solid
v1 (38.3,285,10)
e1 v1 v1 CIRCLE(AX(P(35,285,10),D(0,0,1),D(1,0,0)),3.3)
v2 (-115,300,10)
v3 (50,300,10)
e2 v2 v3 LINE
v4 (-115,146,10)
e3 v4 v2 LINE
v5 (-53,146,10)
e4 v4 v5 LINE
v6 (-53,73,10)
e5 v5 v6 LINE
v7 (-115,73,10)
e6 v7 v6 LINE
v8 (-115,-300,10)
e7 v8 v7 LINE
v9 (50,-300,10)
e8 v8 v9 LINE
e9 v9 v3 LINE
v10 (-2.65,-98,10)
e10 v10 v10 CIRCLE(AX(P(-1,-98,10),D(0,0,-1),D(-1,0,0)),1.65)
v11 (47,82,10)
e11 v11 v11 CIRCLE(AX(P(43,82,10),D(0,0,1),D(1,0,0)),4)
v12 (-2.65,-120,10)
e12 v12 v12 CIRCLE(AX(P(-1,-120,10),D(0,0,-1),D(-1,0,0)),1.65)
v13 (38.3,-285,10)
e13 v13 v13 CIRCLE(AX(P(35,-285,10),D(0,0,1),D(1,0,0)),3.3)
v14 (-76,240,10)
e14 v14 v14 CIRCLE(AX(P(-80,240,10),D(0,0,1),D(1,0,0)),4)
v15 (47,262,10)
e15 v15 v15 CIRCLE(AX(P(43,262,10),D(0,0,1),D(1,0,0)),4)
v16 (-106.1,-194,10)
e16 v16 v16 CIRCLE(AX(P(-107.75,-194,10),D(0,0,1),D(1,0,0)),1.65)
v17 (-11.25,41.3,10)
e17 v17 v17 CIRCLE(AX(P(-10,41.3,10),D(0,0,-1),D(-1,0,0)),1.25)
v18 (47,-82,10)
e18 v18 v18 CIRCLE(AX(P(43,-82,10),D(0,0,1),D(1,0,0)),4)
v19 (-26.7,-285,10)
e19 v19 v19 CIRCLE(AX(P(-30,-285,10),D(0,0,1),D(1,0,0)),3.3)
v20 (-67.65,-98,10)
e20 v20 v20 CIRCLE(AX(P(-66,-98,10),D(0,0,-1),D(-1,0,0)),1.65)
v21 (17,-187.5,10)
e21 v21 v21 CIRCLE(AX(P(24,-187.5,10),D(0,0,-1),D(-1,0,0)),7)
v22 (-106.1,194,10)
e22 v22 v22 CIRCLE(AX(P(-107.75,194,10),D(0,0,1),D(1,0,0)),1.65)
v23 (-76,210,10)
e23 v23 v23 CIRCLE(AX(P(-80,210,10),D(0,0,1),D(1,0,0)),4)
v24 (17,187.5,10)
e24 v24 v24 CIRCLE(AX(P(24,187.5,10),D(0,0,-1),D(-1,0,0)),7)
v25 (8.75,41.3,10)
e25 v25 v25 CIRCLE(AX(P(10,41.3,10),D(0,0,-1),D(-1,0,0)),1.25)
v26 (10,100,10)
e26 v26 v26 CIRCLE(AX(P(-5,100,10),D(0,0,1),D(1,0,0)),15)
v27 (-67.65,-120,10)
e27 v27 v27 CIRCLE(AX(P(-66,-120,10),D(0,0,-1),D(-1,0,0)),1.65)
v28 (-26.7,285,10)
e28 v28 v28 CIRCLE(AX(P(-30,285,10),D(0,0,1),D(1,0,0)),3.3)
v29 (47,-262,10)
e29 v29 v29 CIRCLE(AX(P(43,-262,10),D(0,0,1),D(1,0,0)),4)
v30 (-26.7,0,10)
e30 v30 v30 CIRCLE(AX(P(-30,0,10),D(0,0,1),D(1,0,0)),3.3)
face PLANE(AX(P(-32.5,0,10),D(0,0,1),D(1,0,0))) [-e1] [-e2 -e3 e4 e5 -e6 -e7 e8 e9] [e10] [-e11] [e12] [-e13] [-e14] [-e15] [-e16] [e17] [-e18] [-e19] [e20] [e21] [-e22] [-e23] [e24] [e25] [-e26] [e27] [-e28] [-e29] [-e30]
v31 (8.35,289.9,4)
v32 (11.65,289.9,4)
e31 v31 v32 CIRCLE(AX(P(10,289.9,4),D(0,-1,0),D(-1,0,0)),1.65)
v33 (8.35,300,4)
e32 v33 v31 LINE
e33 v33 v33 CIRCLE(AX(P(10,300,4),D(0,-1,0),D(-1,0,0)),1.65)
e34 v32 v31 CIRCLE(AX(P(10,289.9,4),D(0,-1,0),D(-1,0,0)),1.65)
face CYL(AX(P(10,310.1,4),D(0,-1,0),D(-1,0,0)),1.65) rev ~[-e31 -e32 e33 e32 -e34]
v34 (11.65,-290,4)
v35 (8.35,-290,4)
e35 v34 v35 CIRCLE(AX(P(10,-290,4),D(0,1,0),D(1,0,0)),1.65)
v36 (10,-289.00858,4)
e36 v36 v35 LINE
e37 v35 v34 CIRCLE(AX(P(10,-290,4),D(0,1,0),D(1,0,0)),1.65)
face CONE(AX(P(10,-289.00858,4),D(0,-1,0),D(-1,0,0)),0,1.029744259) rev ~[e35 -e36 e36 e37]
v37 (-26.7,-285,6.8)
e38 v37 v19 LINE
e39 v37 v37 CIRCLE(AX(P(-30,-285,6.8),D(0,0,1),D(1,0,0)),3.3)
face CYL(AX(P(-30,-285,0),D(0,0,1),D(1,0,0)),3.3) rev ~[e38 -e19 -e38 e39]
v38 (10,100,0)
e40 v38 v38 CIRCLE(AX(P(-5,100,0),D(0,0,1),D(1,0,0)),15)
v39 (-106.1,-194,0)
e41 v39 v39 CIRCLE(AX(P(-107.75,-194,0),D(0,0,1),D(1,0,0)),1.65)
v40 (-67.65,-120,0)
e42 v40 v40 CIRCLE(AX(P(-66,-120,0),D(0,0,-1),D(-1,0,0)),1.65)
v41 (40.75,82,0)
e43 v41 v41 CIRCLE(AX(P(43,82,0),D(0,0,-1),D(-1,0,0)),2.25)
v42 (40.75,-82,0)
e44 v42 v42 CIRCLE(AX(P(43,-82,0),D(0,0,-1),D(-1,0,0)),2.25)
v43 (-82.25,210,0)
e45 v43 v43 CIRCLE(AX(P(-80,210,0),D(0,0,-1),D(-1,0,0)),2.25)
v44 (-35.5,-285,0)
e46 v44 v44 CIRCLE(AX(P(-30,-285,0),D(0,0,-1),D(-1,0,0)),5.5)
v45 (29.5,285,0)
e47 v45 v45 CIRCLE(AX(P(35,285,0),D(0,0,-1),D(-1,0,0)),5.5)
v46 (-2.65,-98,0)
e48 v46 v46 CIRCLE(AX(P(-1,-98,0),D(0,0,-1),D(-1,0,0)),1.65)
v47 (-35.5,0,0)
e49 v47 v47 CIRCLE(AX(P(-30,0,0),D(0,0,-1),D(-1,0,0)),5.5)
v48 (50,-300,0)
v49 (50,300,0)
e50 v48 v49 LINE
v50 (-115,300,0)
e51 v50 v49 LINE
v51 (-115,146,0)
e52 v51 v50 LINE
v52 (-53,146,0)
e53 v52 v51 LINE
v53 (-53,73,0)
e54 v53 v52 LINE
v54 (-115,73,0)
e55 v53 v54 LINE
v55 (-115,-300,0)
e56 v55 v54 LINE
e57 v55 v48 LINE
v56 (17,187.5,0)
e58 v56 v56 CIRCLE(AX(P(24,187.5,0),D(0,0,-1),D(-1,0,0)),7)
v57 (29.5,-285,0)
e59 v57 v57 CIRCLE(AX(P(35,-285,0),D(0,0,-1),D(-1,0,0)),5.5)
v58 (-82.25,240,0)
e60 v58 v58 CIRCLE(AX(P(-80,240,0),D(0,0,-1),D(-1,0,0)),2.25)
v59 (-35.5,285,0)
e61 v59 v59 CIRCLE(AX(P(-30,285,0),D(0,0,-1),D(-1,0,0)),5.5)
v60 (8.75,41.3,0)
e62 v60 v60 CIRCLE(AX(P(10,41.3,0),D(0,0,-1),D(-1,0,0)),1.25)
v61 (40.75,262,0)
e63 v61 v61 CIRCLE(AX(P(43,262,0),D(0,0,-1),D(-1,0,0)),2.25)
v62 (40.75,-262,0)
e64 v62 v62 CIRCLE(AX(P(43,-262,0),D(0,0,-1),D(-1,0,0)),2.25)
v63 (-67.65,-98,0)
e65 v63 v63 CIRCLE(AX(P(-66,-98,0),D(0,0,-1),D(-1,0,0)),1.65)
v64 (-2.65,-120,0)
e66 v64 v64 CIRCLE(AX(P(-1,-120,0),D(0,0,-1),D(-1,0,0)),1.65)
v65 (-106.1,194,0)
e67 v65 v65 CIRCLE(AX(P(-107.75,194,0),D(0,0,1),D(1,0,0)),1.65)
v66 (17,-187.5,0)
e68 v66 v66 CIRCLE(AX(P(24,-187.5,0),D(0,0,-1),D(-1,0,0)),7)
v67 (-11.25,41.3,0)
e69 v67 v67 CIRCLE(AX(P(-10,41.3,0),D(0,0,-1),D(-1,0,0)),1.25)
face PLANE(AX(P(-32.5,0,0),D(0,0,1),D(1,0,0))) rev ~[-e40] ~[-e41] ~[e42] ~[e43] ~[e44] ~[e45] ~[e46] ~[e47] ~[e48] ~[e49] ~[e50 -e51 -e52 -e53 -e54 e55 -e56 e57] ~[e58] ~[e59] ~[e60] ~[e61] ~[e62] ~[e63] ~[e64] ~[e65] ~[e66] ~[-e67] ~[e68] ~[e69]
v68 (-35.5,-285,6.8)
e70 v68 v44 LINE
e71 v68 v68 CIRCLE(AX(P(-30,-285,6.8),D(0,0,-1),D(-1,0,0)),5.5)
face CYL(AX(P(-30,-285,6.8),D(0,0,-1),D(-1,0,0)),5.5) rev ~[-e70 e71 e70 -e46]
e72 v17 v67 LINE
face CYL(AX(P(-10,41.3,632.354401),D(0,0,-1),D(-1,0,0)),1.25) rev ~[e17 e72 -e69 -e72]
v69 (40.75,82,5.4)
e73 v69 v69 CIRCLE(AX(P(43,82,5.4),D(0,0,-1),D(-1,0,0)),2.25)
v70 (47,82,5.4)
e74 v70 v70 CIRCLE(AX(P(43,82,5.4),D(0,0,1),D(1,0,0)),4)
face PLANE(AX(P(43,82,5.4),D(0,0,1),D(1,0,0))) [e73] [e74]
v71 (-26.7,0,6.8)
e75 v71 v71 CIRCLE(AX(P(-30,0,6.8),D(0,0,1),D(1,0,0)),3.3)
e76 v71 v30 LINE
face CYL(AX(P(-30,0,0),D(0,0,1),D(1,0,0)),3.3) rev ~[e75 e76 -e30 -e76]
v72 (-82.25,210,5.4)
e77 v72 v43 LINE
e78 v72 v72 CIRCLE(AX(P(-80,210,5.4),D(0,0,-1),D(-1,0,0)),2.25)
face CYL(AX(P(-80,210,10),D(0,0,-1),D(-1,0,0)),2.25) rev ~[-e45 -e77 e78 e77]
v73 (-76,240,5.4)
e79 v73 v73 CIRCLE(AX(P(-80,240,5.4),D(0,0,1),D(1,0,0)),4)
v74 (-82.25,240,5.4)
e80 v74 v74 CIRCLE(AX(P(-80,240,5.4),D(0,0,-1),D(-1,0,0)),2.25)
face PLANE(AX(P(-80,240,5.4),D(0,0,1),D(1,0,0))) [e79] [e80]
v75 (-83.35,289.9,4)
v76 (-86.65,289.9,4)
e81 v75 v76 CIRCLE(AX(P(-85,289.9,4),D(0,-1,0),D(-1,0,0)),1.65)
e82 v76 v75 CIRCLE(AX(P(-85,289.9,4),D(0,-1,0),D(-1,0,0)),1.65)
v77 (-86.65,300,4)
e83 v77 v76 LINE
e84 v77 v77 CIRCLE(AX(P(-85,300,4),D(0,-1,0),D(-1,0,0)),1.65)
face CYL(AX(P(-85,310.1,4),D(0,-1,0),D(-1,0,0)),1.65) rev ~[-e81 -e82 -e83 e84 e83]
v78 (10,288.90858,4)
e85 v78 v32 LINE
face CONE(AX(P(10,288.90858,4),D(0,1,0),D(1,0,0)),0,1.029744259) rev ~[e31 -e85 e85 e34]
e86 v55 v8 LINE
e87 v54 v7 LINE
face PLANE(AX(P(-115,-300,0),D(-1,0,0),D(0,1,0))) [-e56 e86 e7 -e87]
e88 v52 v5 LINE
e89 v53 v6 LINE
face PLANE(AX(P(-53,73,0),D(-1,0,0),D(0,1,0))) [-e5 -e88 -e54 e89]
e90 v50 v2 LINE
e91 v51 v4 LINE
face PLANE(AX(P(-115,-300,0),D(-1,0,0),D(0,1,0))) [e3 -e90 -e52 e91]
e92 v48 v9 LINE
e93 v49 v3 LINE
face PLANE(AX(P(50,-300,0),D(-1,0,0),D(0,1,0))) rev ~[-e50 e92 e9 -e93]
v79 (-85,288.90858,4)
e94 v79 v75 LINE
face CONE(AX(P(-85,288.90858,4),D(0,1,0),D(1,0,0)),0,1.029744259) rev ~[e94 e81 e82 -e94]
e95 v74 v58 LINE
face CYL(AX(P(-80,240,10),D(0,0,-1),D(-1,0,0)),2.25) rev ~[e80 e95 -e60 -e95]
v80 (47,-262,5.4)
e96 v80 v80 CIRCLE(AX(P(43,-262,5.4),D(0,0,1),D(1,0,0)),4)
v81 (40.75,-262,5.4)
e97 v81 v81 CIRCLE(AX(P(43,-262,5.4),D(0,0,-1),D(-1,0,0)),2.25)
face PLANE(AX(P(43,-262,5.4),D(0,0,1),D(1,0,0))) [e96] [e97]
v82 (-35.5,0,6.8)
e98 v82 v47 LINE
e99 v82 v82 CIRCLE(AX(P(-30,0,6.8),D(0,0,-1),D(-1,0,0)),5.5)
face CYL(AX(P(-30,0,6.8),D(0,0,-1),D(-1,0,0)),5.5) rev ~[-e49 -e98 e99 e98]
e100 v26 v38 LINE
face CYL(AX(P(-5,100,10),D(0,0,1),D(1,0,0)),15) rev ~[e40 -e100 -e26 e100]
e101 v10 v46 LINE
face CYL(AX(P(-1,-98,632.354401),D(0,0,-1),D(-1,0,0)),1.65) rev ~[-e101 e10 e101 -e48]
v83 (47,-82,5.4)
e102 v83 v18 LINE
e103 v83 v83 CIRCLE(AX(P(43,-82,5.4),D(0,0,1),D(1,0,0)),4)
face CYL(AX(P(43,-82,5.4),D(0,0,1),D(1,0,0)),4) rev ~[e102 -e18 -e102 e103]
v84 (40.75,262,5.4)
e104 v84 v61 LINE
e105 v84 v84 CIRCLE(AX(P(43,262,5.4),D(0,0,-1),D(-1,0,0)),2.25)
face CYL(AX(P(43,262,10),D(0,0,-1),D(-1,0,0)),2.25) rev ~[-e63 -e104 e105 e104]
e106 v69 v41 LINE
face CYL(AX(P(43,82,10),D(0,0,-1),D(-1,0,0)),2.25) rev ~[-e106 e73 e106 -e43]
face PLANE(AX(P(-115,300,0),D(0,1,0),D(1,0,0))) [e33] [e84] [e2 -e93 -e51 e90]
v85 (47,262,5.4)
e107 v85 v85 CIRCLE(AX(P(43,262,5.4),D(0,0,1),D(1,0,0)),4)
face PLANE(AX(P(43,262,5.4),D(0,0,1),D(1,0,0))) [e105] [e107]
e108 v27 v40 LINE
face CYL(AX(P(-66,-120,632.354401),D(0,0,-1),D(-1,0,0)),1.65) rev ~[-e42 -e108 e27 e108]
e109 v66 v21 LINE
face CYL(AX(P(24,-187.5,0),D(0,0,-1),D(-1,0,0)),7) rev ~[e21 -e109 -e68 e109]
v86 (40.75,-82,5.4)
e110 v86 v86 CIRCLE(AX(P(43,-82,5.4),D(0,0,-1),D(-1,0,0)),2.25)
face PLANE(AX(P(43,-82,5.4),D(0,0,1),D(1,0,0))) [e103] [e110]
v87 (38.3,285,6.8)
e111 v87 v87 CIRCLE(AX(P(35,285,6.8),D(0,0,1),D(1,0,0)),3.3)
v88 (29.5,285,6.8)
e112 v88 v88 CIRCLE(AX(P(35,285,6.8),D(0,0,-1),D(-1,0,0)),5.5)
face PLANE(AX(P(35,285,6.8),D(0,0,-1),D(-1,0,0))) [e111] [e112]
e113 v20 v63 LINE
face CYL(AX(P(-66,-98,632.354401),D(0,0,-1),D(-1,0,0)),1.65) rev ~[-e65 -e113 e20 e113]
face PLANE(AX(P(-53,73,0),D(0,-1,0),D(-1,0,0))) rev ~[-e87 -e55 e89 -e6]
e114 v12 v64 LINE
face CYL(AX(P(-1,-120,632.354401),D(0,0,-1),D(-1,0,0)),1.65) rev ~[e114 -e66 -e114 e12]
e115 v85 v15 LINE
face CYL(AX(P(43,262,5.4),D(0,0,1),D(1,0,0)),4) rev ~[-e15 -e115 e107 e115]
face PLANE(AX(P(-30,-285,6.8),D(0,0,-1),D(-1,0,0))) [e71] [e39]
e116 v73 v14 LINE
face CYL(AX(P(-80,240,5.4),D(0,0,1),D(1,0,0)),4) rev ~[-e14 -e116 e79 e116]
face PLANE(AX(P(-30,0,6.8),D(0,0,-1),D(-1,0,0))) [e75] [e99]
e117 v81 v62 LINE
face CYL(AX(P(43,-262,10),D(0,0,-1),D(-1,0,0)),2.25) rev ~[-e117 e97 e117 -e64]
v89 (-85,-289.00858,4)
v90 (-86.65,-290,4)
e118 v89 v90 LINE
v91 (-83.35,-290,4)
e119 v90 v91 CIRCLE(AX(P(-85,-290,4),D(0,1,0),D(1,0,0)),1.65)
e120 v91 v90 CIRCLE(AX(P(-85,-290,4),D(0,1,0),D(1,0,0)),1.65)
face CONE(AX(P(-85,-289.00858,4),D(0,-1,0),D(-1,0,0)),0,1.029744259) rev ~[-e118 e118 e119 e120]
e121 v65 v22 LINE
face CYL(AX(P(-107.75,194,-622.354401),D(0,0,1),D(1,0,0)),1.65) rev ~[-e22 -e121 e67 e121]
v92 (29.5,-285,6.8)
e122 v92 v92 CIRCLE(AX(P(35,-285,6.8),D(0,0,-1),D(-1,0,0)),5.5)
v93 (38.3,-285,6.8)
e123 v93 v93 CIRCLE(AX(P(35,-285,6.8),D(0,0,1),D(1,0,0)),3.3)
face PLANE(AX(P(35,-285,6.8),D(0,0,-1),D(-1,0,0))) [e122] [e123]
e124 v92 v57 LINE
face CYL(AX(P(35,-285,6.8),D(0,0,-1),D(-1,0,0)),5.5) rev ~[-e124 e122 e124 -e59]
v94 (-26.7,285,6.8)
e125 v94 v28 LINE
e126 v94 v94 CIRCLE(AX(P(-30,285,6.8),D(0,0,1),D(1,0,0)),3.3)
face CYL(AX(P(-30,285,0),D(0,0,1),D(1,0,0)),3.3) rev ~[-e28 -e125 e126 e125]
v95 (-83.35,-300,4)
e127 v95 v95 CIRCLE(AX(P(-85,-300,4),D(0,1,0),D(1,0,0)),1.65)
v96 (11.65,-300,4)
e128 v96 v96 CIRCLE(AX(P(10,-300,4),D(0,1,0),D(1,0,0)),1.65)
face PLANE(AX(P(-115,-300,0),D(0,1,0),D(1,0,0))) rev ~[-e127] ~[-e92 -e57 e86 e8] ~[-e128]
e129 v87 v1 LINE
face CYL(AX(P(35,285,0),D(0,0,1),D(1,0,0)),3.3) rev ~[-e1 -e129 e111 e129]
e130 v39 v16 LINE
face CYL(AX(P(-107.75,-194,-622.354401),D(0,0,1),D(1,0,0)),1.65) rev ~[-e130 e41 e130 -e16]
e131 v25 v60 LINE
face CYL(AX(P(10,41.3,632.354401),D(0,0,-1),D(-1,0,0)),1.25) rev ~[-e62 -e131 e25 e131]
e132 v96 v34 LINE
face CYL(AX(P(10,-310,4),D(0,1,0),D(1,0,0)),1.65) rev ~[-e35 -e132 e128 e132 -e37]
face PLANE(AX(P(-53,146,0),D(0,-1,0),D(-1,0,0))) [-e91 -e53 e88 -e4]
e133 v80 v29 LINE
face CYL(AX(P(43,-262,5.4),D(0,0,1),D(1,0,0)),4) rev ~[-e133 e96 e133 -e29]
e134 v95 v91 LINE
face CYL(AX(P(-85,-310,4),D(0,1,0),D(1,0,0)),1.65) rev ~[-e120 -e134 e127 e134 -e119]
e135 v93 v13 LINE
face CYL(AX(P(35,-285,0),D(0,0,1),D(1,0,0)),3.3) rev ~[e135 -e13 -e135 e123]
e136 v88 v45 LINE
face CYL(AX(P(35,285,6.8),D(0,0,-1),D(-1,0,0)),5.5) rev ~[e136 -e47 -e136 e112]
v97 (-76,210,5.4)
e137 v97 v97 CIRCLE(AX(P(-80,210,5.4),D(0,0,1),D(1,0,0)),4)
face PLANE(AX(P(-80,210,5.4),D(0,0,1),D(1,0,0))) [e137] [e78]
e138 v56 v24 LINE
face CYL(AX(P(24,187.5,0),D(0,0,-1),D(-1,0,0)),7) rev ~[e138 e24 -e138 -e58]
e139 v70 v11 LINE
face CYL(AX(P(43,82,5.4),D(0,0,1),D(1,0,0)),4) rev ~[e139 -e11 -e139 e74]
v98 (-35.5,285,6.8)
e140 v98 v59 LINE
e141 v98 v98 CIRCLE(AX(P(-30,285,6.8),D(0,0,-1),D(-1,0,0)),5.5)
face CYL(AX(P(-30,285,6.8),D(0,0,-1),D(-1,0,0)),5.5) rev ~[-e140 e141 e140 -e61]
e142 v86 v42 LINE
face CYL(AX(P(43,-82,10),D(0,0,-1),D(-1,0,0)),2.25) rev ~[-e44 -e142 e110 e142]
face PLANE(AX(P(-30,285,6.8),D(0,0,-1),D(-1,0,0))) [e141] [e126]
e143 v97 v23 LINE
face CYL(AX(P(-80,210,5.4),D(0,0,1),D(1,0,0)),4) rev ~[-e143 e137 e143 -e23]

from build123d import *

# Parameters (mm, degrees)
SKETCH_1_W                  = 165
SKETCH_1_H                  = 600
EXTRUDE_1_DEPTH             = 10
SKETCH_5_R                  = 15
CUT_EXTRUDE_1_DEPTH         = 322.442063209
HOLE_WIZARD_M4_1_D          = 3.3
HOLE_WIZARD_M3_1_D          = 2.5
HOLE_WIZARD_M4_3_D          = 3.3
SKETCH_18_R                 = 7
CUT_EXTRUDE_2_DEPTH         = 322.442063209
HOLE_WIZARD_M4_4_D          = 3.3
HOLE_WIZARD_M4_4_DEPTH      = 10
HOLE_WIZARD_M4_4_TIP        = 0.991420021
HOLE_WIZARD_M4_5_D          = 3.3
HOLE_WIZARD_M4_5_DEPTH      = 10.1
HOLE_WIZARD_M4_5_TIP        = 0.991420021
HOLE_WIZARD_6_D             = 4.5
HOLE_WIZARD_6_CBORE_D       = 8
HOLE_WIZARD_6_CBORE_DEPTH   = 4.6
SKETCH_27_W                 = 71.16849895
SKETCH_27_H                 = 73
CUT_EXTRUDE_3_DEPTH         = 322.442063209
HOLE_WIZARD_5_D             = 4.5
HOLE_WIZARD_5_CBORE_D       = 8
HOLE_WIZARD_5_CBORE_DEPTH   = 4.6
HOLE_WIZARD_6_2_D           = 6.6
HOLE_WIZARD_6_2_CBORE_D     = 11
HOLE_WIZARD_6_2_CBORE_DEPTH = 6.8


with BuildPart() as part:
    # 草图1 → 凸台-拉伸1 (new body)
    with BuildSketch(Plane.XY):
        with Locations((-32.5, 0)):
            Rectangle(SKETCH_1_W, SKETCH_1_H)
    extrude(amount=EXTRUDE_1_DEPTH)

    # 草图5 → 切除-拉伸1 (cut, through all)
    with BuildSketch(Plane.XY.offset(10)):
        with Locations((-5, 100)):
            Circle(SKETCH_5_R)
    extrude(amount=-CUT_EXTRUDE_1_DEPTH, mode=Mode.SUBTRACT)

    # M4 螺纹孔1 (through all)
    with Locations(Plane.XY.offset(10)):
        with Locations((-66, -120), (-1, -98), (-1, -120), (-66, -98)):
            Hole(HOLE_WIZARD_M4_1_D / 2)

    # M3 螺纹孔1 (through all)
    with Locations(Plane.XY.offset(10)):
        with Locations((-10, 41.3), (10, 41.3)):
            Hole(HOLE_WIZARD_M3_1_D / 2)

    # M4 螺纹孔3 (through all)
    with Locations(Plane(origin=(0, 0, 0), x_dir=(-1, 0, 0), z_dir=(0, 0, -1))):
        with Locations((107.75, 193.999999998), (107.75, -194.000000002)):
            Hole(HOLE_WIZARD_M4_3_D / 2)

    # 草图18 → 切除-拉伸2 (cut, through all)
    with BuildSketch(Plane(origin=(0, 0, 0), x_dir=(-1, 0, 0), z_dir=(0, 0, -1))):
        with Locations((-24, 187.5)):
            Circle(SKETCH_18_R)
        with Locations((-24, -187.5)):
            Circle(SKETCH_18_R)
    extrude(amount=-CUT_EXTRUDE_2_DEPTH, mode=Mode.SUBTRACT)

    # M4 螺纹孔4
    with Locations(Plane(origin=(0, -300, 0), x_dir=(-1, 0, 0), z_dir=(0, -1, 0))):
        with Locations((-10, -4), (85, -4)):
            Hole(HOLE_WIZARD_M4_4_D / 2, depth=HOLE_WIZARD_M4_4_DEPTH)
            with Locations((0, 0, -(HOLE_WIZARD_M4_4_DEPTH + HOLE_WIZARD_M4_4_TIP / 2))):  # 118° drill point
                Cone(0, HOLE_WIZARD_M4_4_D / 2, HOLE_WIZARD_M4_4_TIP, mode=Mode.SUBTRACT)

    # M4 螺纹孔5
    with Locations(Plane(origin=(0, 300, 0), x_dir=(1, 0, 0), z_dir=(0, 1, 0))):
        with Locations((-85, -4), (10, -4)):
            Hole(HOLE_WIZARD_M4_5_D / 2, depth=HOLE_WIZARD_M4_5_DEPTH)
            with Locations((0, 0, -(HOLE_WIZARD_M4_5_DEPTH + HOLE_WIZARD_M4_5_TIP / 2))):  # 118° drill point
                Cone(0, HOLE_WIZARD_M4_5_D / 2, HOLE_WIZARD_M4_5_TIP, mode=Mode.SUBTRACT)

    # Hole Wizard 6 (through all)
    with Locations(Plane.XY.offset(10)):
        with Locations((43, 262), (43, 82), (43, -82), (43, -262)):
            CounterBoreHole(HOLE_WIZARD_6_D / 2, HOLE_WIZARD_6_CBORE_D / 2, HOLE_WIZARD_6_CBORE_DEPTH)

    # 草图27 → 切除-拉伸3 (cut, through all)
    with BuildSketch(Plane(origin=(0, 0, 0), x_dir=(-1, 0, 0), z_dir=(0, 0, -1))):
        with Locations((88.584249475, 109.5)):
            Rectangle(SKETCH_27_W, SKETCH_27_H)
    extrude(amount=-CUT_EXTRUDE_3_DEPTH, mode=Mode.SUBTRACT)

    # 打孔尺寸根据内六角圆柱头螺钉的类型5 (through all)
    with Locations(Plane.XY.offset(10)):
        with Locations((-80, 240), (-80, 210)):
            CounterBoreHole(HOLE_WIZARD_5_D / 2, HOLE_WIZARD_5_CBORE_D / 2, HOLE_WIZARD_5_CBORE_DEPTH)

    # Hole Wizard 6 2 (through all)
    with Locations(Plane(origin=(0, 0, 0), x_dir=(-1, 0, 0), z_dir=(0, 0, -1))):
        with Locations((30.000000001, 285), (-35, 285), (30.000000001, 2e-09), (30.000000001, -284.999999998), (-35, -284.999999998)):
            CounterBoreHole(HOLE_WIZARD_6_2_D / 2, HOLE_WIZARD_6_2_CBORE_D / 2, HOLE_WIZARD_6_2_CBORE_DEPTH)


solid = part.part
